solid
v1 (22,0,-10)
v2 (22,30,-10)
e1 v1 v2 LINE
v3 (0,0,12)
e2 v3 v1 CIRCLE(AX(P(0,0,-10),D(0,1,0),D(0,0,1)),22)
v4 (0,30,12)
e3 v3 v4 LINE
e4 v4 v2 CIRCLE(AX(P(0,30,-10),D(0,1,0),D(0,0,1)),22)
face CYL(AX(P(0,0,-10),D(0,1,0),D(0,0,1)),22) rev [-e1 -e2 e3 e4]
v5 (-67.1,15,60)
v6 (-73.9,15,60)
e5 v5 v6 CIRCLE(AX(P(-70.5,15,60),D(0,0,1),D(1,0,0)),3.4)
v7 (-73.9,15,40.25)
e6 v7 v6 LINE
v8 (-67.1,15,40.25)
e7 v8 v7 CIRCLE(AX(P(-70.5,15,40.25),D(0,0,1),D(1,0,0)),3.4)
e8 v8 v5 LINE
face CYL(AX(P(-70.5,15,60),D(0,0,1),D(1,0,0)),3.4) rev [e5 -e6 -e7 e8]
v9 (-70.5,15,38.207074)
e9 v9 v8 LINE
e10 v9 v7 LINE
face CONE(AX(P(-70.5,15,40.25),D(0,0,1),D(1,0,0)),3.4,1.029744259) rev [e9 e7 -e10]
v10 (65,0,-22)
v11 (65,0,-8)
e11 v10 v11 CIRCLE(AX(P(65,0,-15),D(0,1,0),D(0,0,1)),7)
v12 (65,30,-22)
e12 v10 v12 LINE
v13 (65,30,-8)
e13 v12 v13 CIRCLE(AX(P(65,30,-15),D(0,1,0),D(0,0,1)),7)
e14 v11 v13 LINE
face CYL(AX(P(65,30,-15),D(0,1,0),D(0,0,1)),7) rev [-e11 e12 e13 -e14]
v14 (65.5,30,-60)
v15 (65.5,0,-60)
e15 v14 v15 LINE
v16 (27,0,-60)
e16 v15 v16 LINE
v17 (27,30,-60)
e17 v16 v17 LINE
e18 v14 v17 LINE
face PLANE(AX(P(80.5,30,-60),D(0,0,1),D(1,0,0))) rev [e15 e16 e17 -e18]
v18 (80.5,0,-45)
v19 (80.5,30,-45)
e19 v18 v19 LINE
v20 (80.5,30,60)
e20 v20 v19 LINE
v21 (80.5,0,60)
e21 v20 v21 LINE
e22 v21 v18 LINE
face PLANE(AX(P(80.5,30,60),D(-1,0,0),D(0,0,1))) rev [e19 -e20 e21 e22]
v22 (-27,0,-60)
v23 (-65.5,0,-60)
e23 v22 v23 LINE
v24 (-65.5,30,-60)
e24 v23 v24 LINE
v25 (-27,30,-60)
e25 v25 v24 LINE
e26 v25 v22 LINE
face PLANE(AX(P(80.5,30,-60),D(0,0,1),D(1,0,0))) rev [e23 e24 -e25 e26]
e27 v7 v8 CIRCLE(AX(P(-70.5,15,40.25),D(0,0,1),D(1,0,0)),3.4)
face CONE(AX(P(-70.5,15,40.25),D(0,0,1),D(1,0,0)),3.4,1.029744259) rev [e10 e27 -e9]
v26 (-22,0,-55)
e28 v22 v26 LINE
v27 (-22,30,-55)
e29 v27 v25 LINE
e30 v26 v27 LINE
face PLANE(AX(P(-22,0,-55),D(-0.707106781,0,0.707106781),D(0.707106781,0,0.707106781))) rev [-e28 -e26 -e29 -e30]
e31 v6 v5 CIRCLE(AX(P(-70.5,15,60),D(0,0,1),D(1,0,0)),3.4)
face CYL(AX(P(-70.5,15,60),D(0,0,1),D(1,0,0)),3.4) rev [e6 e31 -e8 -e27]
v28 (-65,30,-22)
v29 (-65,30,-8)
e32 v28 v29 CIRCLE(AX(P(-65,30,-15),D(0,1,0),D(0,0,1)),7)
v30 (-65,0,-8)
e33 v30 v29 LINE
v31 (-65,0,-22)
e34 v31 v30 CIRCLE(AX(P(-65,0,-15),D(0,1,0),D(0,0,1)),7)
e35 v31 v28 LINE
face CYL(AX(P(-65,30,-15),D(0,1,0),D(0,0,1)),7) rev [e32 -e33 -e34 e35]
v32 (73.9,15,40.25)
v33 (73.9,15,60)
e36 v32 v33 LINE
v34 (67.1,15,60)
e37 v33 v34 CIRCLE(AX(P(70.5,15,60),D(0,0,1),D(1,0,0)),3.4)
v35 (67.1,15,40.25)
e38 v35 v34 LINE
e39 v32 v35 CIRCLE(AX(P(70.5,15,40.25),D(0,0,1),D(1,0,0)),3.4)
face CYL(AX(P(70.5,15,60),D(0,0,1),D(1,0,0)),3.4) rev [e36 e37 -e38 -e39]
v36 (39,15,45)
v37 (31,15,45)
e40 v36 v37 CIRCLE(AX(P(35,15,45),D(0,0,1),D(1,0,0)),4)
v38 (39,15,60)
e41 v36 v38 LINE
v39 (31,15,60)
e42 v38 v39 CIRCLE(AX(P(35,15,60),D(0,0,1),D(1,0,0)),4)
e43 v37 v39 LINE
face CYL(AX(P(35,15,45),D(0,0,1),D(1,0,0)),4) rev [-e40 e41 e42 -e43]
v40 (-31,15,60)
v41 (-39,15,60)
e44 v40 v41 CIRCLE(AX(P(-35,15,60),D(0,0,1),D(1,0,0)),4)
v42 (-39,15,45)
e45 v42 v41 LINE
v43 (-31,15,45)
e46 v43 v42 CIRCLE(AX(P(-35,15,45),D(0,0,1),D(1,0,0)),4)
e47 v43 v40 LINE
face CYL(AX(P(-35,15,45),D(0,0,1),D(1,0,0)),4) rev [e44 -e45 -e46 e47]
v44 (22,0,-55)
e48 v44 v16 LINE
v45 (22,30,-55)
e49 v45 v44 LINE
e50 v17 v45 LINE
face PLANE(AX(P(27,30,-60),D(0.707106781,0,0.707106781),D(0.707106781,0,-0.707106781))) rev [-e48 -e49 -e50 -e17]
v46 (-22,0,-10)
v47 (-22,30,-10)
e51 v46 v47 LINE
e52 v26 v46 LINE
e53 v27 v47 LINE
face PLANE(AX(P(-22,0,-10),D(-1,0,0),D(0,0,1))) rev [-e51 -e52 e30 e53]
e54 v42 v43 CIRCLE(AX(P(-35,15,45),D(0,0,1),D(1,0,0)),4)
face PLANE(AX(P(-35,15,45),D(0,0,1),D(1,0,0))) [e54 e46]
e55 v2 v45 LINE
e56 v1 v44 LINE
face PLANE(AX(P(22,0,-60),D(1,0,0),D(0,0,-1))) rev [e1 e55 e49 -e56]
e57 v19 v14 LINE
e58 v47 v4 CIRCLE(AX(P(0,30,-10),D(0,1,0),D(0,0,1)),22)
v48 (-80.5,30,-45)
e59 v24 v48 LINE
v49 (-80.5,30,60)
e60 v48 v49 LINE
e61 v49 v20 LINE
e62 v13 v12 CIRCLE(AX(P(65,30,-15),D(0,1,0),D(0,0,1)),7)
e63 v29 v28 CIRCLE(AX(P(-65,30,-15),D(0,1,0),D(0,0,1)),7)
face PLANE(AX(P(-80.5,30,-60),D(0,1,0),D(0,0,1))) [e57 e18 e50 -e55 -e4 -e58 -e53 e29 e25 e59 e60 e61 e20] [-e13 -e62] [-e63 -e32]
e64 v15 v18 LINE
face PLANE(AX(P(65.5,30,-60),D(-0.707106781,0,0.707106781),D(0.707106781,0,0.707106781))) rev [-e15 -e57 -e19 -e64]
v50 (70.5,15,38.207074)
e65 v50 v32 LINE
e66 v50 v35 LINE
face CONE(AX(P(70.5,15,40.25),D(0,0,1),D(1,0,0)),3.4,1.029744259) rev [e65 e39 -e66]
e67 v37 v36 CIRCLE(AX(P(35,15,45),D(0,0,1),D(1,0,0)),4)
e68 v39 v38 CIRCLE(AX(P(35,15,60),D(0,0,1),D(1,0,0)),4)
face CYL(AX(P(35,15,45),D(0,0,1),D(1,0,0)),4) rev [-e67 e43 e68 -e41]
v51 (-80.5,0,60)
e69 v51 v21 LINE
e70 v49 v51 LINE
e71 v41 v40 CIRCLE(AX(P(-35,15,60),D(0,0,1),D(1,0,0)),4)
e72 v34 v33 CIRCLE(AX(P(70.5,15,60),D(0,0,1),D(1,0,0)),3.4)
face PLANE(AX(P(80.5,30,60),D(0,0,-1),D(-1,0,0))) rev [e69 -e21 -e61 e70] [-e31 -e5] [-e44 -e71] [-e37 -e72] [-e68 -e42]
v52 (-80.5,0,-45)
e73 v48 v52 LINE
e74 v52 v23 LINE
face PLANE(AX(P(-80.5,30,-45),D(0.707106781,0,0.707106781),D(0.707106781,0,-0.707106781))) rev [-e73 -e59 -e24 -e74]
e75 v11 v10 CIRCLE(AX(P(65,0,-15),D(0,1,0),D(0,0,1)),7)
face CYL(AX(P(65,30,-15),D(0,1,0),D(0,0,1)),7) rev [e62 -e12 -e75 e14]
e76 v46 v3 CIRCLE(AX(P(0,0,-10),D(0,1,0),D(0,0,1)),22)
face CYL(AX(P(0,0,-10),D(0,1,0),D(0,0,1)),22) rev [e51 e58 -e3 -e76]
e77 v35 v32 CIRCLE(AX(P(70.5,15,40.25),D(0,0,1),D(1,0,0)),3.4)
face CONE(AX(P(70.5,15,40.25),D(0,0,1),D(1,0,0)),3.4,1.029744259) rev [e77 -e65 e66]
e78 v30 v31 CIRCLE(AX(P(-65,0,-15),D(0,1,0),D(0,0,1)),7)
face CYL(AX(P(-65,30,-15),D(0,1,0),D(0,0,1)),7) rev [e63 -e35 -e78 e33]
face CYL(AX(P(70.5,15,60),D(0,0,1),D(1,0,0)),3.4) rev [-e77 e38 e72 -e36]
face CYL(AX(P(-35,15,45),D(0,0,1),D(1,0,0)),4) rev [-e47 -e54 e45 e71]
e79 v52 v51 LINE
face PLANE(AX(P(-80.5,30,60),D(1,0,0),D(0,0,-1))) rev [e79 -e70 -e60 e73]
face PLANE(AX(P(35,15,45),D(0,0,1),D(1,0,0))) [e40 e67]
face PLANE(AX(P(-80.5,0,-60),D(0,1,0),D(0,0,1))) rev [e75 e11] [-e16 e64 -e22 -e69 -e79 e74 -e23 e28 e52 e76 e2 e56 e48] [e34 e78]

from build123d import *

# Parameters (mm, degrees)
SKETCH1_W             = 161
SKETCH1_H             = 120
BOSS_EXTRUDE1_DEPTH   = 30
CUT_EXTRUDE1_DEPTH    = 105.786688086
M16_TAPPED_HOLE1_D    = 14
M8_TAPPED_HOLE1_D     = 6.8
M8_TAPPED_HOLE1_DEPTH = 19.75
M8_TAPPED_HOLE1_TIP   = 2.042926105
SKETCH7_R             = 4
CUT_EXTRUDE2_DEPTH    = 15
CHAMFER1_SIZE         = 15
CHAMFER2_SIZE         = 5


with BuildPart() as part:
    # Sketch1 → Boss-Extrude1 (new body)
    with BuildSketch(Plane(origin=(0, 0, 0), x_dir=(1, 0, 0), z_dir=(0, 1, 0))):
        Rectangle(SKETCH1_W, SKETCH1_H)
    extrude(amount=BOSS_EXTRUDE1_DEPTH)

    # Sketch2 → Cut-Extrude1 (cut, through all)
    with BuildSketch(Plane(origin=(0, 30, 0), x_dir=(1, 0, 0), z_dir=(0, 1, 0))):
        with BuildLine():
            Line((-22, 10), (-22, 60))
            Line((-22, 60), (22, 60))
            Line((22, 60), (22, 10))
            ThreePointArc((22, 10), (0, -12), (-22, 10))
        make_face()
    extrude(amount=-CUT_EXTRUDE1_DEPTH, mode=Mode.SUBTRACT)

    # M16 Tapped Hole1 (through all)
    with Locations(Plane(origin=(0, 30, 0), x_dir=(-1, 0, 0), z_dir=(0, 1, 0))):
        with Locations((65, -15), (-65, -15)):
            Hole(M16_TAPPED_HOLE1_D / 2)

    # M8 Tapped Hole1
    with Locations(Plane.XY.offset(60)):
        with Locations((70.5, 15), (-70.5, 15)):
            Hole(M8_TAPPED_HOLE1_D / 2, depth=M8_TAPPED_HOLE1_DEPTH)
            with Locations((0, 0, -(M8_TAPPED_HOLE1_DEPTH + M8_TAPPED_HOLE1_TIP / 2))):  # 118° drill point
                Cone(0, M8_TAPPED_HOLE1_D / 2, M8_TAPPED_HOLE1_TIP, mode=Mode.SUBTRACT)

    # Sketch7 → Cut-Extrude2 (cut)
    with BuildSketch(Plane.XY.offset(60)):
        with Locations((-35, 15)):
            Circle(SKETCH7_R)
        with Locations((35, 15)):
            Circle(SKETCH7_R)
    extrude(amount=-CUT_EXTRUDE2_DEPTH, mode=Mode.SUBTRACT)

    # Chamfer1
    chamfer1_edges = [part.edges().sort_by_distance(p)[0] for p in [
        (-80.5, 15, -60),
        (80.5, 15, -60),
    ]]
    chamfer(chamfer1_edges, length=CHAMFER1_SIZE)

    # Chamfer2
    chamfer2_edges = [part.edges().sort_by_distance(p)[0] for p in [
        (-22, 15, -60),
        (22, 15, -60),
    ]]
    chamfer(chamfer2_edges, length=CHAMFER2_SIZE)


solid = part.part
